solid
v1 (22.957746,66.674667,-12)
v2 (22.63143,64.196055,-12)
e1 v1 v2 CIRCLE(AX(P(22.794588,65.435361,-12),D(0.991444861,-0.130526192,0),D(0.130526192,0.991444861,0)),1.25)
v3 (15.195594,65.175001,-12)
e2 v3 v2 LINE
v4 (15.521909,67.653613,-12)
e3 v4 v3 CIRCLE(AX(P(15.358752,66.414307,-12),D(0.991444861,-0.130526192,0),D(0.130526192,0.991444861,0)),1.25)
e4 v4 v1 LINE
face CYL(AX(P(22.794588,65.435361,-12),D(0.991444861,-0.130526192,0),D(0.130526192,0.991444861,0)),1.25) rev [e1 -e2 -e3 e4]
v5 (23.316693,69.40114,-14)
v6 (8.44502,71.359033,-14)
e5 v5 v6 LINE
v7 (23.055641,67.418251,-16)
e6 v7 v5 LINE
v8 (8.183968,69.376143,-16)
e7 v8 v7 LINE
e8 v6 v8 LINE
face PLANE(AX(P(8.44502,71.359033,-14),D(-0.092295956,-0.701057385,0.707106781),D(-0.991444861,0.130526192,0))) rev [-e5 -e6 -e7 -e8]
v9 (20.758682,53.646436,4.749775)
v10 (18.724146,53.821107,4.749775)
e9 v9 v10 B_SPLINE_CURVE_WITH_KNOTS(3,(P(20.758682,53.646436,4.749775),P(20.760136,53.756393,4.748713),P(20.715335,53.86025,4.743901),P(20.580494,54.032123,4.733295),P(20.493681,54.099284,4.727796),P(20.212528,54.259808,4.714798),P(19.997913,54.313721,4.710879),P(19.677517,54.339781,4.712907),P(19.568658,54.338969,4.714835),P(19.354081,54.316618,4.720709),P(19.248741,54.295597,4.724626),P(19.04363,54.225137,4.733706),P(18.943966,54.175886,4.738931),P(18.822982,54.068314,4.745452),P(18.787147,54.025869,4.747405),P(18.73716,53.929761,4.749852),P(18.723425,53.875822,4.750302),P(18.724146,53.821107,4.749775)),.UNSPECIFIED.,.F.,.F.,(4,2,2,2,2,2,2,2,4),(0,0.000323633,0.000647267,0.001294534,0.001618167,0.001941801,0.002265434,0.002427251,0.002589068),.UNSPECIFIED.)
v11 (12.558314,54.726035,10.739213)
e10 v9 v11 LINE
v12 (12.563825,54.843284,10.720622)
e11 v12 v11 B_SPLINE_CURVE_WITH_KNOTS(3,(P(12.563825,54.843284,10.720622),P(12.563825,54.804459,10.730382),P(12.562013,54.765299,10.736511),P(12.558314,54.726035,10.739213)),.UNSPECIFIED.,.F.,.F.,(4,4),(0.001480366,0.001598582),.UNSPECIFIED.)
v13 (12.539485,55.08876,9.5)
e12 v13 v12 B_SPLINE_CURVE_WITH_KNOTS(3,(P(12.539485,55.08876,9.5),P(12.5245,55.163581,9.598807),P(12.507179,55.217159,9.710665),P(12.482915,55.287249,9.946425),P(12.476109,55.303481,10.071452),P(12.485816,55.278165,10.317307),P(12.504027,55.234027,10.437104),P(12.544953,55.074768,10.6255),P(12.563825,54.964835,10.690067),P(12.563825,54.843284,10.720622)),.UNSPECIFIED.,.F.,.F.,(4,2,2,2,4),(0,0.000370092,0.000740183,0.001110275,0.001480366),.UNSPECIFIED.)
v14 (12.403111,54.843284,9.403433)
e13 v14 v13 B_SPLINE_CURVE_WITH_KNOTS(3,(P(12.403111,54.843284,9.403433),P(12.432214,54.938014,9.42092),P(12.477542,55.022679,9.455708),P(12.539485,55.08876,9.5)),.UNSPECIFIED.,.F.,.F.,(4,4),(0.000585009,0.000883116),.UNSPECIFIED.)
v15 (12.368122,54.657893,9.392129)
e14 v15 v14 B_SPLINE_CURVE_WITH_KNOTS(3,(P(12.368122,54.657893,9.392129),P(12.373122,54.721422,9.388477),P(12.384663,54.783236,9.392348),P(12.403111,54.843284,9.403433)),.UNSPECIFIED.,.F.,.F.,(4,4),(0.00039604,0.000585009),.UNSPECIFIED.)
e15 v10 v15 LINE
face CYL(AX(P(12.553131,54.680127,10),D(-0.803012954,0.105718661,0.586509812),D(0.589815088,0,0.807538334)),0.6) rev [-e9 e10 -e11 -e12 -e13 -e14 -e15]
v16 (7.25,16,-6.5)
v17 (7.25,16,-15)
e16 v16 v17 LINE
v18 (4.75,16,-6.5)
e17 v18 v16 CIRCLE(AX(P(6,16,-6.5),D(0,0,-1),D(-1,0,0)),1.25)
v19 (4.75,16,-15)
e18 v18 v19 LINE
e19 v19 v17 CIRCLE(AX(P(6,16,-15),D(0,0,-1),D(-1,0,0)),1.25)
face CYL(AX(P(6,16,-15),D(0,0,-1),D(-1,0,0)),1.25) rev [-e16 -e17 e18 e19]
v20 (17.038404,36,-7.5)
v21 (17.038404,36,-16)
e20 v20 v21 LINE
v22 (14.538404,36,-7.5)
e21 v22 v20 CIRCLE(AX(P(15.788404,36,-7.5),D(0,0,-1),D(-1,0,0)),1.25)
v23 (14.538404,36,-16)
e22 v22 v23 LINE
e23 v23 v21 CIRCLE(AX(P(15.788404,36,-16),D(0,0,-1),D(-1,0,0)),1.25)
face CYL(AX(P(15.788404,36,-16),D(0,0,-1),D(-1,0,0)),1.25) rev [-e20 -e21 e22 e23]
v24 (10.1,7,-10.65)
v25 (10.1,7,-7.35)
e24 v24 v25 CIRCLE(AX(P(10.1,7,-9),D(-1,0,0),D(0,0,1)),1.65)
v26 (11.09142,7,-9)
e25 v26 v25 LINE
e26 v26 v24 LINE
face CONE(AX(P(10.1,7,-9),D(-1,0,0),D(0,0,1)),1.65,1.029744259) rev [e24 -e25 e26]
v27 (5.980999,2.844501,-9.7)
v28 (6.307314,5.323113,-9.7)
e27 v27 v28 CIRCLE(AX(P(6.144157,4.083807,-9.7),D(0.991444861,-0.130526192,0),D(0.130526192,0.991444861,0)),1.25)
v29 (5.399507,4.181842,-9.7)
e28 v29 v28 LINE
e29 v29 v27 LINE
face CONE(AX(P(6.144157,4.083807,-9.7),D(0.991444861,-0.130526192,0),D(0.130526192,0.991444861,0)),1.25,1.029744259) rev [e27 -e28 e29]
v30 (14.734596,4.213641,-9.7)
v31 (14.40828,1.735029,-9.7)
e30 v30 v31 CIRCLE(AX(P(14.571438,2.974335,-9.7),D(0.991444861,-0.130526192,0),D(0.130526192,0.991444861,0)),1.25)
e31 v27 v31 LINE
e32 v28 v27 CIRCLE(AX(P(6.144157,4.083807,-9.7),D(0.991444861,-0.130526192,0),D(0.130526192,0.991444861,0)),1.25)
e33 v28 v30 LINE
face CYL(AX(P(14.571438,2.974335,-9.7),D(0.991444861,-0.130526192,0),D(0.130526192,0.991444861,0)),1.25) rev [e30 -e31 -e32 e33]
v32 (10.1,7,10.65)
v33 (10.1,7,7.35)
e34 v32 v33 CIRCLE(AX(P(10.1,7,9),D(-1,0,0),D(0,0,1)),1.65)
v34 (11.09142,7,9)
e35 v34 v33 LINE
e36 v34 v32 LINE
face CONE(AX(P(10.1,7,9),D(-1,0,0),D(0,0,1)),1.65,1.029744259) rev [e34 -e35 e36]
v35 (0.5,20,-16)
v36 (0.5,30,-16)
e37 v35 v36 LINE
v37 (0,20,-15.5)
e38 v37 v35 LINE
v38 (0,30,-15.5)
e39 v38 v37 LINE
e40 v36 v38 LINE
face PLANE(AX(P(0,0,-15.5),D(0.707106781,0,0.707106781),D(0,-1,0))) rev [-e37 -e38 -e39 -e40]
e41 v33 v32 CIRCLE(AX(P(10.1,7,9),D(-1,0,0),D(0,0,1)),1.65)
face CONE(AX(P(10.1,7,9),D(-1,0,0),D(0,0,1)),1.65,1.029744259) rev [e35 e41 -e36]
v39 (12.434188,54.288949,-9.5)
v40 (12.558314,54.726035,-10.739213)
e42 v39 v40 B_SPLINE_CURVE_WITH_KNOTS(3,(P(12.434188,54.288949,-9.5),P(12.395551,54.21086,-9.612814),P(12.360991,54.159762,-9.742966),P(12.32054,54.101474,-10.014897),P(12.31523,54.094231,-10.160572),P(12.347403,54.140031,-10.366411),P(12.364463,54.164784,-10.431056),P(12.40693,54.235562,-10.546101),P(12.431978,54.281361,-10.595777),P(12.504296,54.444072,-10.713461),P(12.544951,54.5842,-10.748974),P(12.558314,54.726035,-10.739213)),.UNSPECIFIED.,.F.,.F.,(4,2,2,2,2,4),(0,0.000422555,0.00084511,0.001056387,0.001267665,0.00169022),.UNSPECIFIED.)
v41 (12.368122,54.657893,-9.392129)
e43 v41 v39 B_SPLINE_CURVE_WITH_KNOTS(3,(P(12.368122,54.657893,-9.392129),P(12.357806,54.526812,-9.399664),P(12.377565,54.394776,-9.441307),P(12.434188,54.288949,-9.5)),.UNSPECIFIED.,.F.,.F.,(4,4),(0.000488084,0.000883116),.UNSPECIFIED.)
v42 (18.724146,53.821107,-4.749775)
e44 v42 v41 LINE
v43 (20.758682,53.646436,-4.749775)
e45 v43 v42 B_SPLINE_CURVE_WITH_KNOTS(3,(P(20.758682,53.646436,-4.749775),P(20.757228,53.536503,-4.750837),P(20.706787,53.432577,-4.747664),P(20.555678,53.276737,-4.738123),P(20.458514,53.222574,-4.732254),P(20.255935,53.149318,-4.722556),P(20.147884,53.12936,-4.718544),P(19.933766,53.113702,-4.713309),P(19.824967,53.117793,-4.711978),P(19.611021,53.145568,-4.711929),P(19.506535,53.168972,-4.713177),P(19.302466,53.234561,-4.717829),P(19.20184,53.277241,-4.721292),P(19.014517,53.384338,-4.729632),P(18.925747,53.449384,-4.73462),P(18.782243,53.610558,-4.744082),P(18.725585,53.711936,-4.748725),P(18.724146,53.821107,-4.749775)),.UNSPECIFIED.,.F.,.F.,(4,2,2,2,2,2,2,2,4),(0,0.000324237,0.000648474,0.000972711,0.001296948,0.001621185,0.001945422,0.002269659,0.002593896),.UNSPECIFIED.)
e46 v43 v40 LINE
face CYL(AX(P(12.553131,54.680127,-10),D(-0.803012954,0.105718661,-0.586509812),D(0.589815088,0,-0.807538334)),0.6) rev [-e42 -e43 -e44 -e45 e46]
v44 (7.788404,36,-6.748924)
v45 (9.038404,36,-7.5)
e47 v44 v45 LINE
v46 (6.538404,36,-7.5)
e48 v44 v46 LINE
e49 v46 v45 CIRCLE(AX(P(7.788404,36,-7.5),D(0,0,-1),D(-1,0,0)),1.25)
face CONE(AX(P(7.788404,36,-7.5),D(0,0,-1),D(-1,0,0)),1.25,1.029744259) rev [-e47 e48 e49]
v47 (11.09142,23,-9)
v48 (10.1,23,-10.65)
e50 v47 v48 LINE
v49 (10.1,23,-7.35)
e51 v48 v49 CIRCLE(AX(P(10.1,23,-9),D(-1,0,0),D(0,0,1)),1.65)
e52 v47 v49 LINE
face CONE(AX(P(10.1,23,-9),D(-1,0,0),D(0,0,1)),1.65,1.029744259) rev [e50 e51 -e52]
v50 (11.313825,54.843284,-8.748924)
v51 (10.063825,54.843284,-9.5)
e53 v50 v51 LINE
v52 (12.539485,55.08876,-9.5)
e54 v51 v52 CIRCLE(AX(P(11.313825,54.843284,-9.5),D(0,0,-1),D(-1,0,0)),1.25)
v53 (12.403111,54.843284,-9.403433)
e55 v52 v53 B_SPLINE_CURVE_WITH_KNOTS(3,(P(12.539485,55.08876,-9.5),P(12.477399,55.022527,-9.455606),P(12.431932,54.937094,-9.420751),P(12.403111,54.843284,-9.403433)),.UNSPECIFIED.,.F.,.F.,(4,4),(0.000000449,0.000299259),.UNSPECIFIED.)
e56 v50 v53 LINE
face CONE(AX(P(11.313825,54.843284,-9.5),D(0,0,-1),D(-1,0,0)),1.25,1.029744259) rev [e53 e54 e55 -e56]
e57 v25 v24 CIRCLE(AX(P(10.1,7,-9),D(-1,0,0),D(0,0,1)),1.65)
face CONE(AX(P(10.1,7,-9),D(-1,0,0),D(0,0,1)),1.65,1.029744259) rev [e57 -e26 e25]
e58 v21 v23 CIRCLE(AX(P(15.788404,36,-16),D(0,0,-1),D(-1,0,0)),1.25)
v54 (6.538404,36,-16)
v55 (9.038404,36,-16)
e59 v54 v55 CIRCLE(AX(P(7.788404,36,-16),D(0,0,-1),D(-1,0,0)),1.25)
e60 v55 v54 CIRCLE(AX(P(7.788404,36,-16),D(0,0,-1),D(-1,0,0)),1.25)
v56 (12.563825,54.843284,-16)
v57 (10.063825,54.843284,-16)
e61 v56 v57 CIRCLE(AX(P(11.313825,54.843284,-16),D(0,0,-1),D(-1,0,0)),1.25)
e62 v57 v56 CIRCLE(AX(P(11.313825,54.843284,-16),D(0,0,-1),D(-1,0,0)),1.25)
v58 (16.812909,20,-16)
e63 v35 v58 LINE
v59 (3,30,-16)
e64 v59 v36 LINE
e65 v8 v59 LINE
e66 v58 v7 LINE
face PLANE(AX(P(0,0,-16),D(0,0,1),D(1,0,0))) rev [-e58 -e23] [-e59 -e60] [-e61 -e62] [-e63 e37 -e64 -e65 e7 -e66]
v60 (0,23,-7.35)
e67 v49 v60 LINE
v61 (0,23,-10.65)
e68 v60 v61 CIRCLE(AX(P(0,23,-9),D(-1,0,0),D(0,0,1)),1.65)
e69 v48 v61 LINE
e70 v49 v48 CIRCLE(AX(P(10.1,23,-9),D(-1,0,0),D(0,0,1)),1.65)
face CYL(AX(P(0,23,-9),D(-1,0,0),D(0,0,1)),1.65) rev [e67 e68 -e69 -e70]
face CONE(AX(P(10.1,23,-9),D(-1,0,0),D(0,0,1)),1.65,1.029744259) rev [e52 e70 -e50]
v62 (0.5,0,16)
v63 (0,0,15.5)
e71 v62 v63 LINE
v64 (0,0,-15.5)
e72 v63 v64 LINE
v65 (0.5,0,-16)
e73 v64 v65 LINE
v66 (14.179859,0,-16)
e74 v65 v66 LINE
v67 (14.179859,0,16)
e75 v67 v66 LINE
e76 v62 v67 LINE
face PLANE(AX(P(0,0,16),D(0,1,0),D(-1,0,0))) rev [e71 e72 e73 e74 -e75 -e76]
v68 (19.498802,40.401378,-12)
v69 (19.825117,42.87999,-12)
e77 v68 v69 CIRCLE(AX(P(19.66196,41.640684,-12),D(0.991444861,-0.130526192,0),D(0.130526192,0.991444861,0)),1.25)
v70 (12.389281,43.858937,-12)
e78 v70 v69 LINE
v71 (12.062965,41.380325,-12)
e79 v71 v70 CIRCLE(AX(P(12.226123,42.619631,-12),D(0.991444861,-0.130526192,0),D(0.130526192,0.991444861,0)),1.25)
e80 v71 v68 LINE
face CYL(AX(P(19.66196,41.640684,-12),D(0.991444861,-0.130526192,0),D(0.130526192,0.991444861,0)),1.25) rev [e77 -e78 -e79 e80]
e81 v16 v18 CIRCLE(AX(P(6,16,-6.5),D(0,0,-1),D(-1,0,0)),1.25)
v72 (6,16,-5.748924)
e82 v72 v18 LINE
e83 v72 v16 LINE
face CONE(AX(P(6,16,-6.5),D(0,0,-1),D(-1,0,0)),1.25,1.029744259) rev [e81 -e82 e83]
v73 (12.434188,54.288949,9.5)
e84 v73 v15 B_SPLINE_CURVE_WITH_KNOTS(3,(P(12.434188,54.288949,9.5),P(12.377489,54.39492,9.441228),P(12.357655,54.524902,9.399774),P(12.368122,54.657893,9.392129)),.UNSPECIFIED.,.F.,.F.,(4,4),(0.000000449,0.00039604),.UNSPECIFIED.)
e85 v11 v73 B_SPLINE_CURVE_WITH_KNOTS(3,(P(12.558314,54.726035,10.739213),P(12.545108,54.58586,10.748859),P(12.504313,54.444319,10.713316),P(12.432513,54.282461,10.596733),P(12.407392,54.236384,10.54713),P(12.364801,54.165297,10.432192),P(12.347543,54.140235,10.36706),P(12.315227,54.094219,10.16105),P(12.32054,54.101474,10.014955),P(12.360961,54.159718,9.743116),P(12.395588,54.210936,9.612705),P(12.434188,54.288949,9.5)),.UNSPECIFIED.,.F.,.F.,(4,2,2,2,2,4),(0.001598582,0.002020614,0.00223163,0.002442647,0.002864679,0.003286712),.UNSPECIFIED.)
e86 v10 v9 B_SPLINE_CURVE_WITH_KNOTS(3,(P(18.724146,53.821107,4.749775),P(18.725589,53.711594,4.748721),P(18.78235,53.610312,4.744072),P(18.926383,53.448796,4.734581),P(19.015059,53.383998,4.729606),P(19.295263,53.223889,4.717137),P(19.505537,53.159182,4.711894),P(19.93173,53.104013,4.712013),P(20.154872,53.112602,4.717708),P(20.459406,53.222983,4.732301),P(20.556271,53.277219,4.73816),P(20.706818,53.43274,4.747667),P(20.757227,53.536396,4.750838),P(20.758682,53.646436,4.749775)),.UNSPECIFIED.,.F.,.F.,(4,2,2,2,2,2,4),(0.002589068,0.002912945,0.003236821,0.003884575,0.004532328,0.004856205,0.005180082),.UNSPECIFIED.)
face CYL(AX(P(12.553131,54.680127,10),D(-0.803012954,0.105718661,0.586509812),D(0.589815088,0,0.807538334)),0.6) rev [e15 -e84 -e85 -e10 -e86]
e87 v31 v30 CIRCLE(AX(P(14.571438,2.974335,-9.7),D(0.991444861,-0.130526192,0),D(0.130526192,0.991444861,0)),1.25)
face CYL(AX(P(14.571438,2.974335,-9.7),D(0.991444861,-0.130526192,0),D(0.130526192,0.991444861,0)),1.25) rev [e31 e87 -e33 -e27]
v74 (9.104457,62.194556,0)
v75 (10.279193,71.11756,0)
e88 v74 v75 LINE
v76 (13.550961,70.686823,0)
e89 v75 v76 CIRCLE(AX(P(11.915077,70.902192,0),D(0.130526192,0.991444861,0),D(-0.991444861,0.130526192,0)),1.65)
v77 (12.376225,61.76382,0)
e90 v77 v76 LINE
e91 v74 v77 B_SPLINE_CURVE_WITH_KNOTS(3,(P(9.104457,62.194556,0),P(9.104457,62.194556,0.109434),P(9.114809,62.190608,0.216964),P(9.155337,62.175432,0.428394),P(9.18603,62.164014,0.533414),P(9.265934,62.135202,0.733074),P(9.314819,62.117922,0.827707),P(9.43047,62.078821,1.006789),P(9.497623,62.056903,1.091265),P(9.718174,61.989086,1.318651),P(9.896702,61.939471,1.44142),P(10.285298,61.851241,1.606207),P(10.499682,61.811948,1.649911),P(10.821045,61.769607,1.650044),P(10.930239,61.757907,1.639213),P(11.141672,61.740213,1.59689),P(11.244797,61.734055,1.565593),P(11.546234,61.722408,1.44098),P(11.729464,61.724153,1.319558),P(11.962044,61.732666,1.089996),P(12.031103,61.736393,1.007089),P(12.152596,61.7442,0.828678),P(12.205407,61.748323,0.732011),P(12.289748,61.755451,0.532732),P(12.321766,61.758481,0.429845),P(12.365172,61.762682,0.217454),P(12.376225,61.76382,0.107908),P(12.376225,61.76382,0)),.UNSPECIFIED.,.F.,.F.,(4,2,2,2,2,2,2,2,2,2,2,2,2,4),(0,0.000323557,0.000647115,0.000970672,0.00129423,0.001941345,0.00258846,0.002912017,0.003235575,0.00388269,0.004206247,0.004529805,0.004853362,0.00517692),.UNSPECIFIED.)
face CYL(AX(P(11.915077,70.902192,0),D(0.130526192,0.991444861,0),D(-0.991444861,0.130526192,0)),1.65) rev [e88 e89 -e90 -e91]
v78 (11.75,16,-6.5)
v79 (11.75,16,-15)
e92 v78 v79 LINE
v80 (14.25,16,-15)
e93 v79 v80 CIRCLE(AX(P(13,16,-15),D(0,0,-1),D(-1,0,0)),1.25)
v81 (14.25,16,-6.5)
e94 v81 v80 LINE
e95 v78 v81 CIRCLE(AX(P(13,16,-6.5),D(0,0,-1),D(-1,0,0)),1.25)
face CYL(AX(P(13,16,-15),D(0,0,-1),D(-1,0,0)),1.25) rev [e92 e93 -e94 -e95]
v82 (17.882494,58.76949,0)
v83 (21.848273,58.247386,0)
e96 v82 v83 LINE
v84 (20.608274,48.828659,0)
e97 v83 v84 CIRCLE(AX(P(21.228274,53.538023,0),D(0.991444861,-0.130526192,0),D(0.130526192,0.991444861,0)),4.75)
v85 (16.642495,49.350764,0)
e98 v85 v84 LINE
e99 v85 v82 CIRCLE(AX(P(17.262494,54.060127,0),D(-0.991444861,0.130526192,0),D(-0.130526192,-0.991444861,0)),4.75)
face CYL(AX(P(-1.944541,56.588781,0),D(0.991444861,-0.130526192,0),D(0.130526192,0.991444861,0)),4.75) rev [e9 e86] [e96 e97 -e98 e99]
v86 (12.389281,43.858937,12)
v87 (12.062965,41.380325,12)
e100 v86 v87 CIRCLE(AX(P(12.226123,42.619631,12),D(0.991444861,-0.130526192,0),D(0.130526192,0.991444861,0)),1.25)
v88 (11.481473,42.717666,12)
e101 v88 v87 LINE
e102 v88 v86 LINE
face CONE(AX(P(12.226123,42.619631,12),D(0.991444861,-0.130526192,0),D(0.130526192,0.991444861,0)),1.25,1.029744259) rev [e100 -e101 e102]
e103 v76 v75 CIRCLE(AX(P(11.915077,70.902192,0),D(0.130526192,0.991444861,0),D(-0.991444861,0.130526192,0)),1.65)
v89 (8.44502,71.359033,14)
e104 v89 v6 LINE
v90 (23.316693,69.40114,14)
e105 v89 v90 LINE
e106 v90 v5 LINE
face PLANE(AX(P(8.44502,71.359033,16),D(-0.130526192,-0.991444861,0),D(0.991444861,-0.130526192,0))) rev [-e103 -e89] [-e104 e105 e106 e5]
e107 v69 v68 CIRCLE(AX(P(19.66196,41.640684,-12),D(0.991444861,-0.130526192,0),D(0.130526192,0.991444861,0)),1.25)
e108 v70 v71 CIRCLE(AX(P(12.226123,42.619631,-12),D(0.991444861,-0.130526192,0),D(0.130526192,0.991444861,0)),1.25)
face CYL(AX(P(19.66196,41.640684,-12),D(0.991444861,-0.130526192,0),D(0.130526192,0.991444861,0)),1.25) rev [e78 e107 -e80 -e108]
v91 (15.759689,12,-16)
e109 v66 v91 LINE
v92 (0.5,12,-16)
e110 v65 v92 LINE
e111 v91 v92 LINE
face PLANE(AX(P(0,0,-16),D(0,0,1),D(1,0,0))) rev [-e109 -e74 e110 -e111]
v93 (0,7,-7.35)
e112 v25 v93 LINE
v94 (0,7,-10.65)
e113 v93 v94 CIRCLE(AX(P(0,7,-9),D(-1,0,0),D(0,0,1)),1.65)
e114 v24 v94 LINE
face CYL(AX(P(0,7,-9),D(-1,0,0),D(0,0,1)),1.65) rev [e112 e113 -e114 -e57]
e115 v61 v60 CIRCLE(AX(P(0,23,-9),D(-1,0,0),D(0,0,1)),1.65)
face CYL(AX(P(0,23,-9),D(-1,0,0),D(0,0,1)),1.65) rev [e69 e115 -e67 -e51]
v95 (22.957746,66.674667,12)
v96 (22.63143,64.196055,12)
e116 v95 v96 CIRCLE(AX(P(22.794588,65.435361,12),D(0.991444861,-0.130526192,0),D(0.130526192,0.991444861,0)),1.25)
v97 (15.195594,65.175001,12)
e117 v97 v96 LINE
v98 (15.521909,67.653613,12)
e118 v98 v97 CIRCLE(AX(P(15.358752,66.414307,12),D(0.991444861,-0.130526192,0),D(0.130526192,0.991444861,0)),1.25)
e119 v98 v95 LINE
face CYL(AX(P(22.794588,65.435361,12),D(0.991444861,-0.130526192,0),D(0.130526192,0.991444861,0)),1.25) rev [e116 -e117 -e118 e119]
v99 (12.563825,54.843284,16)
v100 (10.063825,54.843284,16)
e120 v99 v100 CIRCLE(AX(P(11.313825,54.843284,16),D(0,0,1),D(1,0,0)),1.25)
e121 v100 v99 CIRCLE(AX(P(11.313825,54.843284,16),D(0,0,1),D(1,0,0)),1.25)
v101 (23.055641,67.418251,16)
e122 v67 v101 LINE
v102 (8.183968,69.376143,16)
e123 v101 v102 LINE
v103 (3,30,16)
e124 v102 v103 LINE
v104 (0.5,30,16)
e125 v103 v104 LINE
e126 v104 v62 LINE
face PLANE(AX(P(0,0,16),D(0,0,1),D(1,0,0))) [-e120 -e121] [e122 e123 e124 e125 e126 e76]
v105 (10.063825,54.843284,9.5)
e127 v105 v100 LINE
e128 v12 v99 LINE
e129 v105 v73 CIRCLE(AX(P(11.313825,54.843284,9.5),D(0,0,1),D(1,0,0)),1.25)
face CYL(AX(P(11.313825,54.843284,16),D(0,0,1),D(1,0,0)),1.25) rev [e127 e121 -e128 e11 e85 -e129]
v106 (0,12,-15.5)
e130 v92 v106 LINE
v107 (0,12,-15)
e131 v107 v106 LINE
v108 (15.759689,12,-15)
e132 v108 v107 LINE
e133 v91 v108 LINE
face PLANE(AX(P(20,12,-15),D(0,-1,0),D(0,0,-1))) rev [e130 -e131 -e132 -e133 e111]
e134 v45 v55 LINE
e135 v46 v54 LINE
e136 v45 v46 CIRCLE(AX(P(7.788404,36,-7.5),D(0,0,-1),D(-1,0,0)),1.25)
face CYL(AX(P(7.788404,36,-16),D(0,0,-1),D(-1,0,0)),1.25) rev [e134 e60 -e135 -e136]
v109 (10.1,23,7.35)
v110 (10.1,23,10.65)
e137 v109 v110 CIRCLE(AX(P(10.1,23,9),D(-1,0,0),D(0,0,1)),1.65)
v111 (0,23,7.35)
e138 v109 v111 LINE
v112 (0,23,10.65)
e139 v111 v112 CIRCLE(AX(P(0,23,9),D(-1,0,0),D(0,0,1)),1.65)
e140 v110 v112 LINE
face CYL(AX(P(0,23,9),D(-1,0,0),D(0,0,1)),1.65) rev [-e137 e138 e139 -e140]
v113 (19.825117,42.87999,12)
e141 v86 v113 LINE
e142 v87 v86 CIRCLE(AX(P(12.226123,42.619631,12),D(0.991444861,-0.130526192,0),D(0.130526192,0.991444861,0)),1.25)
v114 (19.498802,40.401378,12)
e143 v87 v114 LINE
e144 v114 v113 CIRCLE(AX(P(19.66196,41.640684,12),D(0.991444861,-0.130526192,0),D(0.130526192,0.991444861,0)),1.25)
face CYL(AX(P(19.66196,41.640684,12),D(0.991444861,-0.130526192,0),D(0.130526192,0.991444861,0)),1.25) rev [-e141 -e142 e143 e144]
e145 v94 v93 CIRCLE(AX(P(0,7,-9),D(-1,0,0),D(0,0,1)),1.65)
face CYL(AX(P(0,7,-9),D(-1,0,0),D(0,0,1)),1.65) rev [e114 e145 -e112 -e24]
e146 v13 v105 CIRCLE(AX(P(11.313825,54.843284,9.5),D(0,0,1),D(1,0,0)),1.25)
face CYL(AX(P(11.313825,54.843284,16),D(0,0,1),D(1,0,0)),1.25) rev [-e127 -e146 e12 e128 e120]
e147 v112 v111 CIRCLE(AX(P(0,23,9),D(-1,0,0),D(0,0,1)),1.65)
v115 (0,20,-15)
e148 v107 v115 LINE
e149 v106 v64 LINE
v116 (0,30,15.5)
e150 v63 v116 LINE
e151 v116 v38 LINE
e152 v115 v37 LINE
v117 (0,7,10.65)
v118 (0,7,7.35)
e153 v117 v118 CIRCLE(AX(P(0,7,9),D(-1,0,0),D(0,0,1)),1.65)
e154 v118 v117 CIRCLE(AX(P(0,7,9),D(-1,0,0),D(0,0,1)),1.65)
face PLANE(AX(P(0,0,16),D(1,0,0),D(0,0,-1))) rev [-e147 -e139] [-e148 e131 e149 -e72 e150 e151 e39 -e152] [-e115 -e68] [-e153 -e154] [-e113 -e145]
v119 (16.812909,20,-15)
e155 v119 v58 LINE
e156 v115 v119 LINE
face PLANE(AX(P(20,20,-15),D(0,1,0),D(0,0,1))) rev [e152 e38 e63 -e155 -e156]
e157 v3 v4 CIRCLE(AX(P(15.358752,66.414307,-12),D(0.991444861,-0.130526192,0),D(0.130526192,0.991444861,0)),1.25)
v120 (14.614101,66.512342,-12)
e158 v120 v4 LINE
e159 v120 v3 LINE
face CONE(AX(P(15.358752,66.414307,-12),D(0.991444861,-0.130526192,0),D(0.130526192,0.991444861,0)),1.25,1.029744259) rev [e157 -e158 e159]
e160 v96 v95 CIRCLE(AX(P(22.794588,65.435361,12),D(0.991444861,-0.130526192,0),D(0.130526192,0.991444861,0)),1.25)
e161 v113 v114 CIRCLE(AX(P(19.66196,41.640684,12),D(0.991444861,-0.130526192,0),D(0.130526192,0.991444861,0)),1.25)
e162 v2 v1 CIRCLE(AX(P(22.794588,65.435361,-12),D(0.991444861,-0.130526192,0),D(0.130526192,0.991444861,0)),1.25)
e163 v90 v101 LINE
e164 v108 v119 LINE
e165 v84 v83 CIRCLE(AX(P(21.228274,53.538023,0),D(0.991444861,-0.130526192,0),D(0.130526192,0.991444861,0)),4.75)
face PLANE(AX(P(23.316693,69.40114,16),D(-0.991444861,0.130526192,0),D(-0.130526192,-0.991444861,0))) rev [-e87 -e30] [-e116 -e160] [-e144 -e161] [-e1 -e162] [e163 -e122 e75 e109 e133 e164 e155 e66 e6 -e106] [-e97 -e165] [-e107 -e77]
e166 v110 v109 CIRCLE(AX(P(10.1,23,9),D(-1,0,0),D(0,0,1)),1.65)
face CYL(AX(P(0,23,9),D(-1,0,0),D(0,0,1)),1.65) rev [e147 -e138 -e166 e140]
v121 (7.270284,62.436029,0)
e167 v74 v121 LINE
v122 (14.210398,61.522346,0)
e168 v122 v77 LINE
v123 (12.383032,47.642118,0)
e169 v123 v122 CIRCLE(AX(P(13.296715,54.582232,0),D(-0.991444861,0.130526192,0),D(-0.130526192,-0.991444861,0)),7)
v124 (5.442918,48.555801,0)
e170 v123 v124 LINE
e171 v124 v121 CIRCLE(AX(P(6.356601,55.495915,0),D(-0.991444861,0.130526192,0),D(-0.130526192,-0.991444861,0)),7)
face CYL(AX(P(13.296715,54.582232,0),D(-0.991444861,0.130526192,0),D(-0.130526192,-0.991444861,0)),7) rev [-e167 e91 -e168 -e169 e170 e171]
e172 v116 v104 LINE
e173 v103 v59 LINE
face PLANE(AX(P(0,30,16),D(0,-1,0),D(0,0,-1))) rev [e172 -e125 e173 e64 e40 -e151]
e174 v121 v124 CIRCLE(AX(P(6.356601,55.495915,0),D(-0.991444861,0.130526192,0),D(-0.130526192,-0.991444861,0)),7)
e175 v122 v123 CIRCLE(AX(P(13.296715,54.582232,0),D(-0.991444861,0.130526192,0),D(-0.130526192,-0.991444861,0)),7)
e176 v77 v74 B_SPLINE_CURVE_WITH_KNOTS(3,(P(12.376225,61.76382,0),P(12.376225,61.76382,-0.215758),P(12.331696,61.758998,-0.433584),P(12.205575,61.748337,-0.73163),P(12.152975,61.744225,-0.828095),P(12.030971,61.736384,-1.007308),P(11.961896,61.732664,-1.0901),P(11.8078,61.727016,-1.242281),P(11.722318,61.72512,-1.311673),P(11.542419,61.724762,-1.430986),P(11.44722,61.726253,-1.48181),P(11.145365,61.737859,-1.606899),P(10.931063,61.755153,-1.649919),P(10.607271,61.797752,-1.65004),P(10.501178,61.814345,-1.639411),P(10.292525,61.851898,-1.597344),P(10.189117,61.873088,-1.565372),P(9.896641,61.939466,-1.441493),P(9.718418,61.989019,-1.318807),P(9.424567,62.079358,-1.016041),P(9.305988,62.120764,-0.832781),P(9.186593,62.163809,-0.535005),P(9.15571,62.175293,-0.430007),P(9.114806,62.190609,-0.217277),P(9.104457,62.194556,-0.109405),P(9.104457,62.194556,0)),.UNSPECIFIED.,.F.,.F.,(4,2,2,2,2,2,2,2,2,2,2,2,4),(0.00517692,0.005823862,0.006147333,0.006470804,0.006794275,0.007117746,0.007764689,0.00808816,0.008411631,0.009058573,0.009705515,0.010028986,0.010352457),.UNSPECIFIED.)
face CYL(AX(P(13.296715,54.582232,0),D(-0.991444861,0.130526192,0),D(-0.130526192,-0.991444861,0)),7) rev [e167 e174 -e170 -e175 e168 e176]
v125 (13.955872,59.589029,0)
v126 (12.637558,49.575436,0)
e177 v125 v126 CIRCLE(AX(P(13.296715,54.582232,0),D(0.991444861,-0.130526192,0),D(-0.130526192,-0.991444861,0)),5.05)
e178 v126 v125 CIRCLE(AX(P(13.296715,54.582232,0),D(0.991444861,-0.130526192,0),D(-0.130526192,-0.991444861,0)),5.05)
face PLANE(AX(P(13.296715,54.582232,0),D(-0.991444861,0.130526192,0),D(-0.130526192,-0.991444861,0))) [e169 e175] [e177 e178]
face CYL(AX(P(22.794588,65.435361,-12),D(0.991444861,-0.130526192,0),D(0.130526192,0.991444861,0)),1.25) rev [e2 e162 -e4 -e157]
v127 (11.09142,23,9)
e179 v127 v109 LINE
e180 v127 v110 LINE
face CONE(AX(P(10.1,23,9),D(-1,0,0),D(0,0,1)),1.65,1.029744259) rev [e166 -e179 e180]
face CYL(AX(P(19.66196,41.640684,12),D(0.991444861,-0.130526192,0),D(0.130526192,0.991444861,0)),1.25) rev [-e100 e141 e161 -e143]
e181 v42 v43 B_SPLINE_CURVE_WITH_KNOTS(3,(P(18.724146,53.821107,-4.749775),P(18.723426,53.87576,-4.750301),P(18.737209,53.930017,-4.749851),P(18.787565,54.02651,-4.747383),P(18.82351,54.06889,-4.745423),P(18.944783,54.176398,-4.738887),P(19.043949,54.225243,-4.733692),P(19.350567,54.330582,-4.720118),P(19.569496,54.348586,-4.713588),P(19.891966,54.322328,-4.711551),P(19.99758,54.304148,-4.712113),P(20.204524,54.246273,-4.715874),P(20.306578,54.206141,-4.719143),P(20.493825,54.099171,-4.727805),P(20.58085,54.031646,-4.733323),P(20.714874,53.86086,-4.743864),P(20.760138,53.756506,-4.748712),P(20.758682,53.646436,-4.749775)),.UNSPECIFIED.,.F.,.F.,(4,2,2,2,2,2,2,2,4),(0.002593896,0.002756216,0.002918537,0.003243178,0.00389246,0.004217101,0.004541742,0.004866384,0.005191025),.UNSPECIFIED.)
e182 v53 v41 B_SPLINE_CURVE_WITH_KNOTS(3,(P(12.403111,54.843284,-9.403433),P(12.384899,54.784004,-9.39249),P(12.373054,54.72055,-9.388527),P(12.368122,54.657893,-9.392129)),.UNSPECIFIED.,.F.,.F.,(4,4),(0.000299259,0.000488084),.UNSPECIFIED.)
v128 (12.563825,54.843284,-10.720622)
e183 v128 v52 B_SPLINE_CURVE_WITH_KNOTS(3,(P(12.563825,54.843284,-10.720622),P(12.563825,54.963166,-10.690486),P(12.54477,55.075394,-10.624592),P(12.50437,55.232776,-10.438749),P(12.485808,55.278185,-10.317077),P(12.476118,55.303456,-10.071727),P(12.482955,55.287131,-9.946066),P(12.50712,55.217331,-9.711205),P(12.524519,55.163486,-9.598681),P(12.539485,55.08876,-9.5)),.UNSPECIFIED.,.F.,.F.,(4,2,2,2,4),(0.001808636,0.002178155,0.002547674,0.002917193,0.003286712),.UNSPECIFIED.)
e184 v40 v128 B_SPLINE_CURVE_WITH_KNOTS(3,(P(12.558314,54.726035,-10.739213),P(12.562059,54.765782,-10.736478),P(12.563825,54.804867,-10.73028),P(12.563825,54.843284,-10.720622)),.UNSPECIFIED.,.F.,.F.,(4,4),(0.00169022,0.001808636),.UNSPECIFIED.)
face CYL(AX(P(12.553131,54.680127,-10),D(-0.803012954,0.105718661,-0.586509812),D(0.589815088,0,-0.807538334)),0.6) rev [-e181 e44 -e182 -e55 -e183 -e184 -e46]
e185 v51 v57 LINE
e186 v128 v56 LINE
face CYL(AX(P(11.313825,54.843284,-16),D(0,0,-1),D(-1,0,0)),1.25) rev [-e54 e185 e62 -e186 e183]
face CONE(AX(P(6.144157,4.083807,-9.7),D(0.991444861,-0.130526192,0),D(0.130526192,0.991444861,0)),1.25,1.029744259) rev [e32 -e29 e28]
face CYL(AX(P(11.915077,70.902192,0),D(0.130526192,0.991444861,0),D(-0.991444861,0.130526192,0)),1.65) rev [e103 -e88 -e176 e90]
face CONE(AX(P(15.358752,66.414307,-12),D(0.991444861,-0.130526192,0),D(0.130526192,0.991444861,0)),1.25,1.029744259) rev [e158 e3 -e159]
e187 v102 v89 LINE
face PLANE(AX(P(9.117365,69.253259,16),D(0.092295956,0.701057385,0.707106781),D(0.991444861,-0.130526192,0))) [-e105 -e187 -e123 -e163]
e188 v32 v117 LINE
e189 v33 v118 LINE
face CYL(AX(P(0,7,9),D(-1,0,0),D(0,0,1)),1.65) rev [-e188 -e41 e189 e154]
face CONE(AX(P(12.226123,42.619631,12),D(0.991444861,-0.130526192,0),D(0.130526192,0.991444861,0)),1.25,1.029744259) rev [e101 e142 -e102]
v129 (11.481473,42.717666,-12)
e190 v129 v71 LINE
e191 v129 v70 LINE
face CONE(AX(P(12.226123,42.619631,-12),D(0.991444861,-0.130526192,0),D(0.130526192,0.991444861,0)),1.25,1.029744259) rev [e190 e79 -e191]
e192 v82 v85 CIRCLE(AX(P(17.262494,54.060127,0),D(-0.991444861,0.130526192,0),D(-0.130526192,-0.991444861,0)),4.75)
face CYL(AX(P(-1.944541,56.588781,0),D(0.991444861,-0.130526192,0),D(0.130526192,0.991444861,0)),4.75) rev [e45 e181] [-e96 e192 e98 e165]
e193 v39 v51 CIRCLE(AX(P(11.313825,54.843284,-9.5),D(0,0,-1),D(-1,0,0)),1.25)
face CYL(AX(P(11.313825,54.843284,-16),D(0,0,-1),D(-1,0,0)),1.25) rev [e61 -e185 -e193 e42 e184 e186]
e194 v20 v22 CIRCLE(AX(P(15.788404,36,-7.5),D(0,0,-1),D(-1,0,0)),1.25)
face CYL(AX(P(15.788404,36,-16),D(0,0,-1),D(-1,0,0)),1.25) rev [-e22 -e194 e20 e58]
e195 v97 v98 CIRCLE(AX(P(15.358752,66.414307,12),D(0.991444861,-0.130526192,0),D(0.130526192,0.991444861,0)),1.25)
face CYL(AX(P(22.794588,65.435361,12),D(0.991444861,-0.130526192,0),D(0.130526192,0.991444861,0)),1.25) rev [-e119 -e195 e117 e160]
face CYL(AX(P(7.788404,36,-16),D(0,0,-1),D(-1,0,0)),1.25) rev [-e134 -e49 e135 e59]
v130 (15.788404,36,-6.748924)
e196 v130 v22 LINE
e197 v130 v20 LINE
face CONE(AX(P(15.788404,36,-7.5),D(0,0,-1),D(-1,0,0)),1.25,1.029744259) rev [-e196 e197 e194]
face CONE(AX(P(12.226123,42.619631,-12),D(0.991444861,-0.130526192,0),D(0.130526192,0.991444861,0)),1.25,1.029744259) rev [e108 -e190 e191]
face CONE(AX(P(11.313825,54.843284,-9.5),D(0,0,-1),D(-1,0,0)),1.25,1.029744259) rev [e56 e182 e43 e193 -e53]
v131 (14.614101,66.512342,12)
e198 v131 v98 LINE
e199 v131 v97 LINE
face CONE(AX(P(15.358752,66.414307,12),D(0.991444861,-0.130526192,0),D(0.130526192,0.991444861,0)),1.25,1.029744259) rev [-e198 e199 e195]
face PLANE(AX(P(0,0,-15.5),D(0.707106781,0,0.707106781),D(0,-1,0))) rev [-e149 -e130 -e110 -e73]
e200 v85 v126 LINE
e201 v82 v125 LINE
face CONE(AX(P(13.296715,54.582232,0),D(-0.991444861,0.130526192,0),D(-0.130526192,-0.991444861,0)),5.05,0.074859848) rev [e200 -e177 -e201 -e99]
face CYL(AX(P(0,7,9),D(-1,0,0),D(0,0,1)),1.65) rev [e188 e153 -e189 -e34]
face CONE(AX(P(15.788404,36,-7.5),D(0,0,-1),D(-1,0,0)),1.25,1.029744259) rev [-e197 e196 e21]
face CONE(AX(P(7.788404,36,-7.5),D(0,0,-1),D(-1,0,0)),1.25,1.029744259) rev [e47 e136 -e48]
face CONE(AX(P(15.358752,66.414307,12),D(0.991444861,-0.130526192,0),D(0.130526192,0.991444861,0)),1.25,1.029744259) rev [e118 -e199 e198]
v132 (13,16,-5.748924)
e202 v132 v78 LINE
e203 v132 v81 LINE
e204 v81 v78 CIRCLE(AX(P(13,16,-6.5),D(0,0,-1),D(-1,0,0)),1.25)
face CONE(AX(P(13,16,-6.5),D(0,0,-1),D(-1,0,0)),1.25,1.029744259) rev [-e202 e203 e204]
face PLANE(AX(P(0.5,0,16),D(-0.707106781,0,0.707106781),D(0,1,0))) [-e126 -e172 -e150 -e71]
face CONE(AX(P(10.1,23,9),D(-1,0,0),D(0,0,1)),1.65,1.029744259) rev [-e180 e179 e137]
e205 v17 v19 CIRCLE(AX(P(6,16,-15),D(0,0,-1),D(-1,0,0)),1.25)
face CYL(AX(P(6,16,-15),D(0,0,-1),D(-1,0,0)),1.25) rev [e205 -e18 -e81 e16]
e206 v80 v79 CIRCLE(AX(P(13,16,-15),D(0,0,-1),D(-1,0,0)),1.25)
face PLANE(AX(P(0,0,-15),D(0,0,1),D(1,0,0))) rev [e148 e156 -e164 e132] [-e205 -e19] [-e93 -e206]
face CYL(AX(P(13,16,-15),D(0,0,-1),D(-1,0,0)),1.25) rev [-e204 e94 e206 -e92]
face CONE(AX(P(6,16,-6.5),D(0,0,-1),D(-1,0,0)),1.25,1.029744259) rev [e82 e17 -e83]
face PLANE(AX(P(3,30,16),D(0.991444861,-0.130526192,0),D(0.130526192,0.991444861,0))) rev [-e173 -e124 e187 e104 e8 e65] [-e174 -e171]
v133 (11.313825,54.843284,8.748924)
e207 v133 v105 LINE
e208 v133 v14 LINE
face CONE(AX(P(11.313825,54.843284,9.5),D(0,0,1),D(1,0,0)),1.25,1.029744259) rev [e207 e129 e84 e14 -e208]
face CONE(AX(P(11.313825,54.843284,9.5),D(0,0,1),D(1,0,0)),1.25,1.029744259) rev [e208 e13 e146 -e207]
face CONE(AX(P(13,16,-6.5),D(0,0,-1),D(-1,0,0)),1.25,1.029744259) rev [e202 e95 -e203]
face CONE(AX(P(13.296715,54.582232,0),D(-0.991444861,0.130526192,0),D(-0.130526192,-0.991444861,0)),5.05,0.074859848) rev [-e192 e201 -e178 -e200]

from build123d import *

# Parameters (mm, degrees)
BOSS_EXTRUDE1_DEPTH    = 16
SKETCH2_R              = 4.75
CUT_EXTRUDE1_DEPTH     = 77.207895426
CHAMFER1_SIZE          = 2
SKETCH3_R              = 7
CUT_EXTRUDE2_DEPTH     = 7
CHAMFER2_SIZE          = 4
CHAMFER2_SIZE2         = 0.3
M3_TAPPED_HOLE2_D      = 2.5
M3_TAPPED_HOLE2_DEPTH  = 7.5
M3_TAPPED_HOLE2_TIP    = 0.751075774
M4_TAPPED_HOLE1_D      = 3.3
M4_TAPPED_HOLE1_DEPTH  = 10.1
M4_TAPPED_HOLE1_TIP    = 0.991420021
CHAMFER3_SIZE          = 0.5
M4_TAPPED_HOLE3_REACH  = 76.329
M4_TAPPED_HOLE3_BORE_R = 1.65
M3_TAPPED_HOLE3_D      = 2.5
M3_TAPPED_HOLE3_DEPTH  = 8.5
M3_TAPPED_HOLE3_TIP    = 0.751075774
M3_TAPPED_HOLE4_D      = 2.5
M3_TAPPED_HOLE4_DEPTH  = 8.5
M3_TAPPED_HOLE4_TIP    = 0.751075774
SKETCH20_W             = 20
SKETCH20_H             = 8
CUT_EXTRUDE3_DEPTH     = 1
M3_TAPPED_HOLE5_D      = 2.5
M3_TAPPED_HOLE5_DEPTH  = 8.5
M3_TAPPED_HOLE5_TIP    = 0.751075774


with BuildPart() as part:
    # Sketch1 → Boss-Extrude1 (new, symmetric)
    with BuildSketch(Plane.XY):
        Polygon((0, 0), (0, 30), (3, 30), (8.445020016, 71.359033179), (23.316692936, 69.401140296), (14.179859481, 0), align=None)
    extrude(amount=BOSS_EXTRUDE1_DEPTH, both=True)

    # Sketch2 → Cut-Extrude1 (cut, through all)
    with BuildSketch(Plane(origin=(13.938275984, -1.835008845, 0), x_dir=(0, 0, -1), z_dir=(0.9914448613738108, -0.1305261922200488, 0))):
        with Locations(Location((0, 55.850843064, 0), (0, 0, 90))):
            Circle(SKETCH2_R)
    extrude(amount=-CUT_EXTRUDE1_DEPTH, mode=Mode.SUBTRACT)

    # Chamfer1
    chamfer1_edges = [part.edges().sort_by_distance(p)[0] for p in [
        (15.880856476, 70.380086738, 16),
        (15.880856476, 70.380086738, -16),
    ]]
    chamfer(chamfer1_edges, length=CHAMFER1_SIZE)

    # Sketch3 → Cut-Extrude2 (cut)
    with BuildSketch(Plane(origin=(-0.933396937, 0.122884038, 0), x_dir=(0, 0, 1), z_dir=(-0.9914448613738109, 0.13052619222004871, 0))):
        with Locations(Location((0, 55.850843064, 0), (0, 0, 270))):
            Circle(SKETCH3_R)
    extrude(amount=-CUT_EXTRUDE2_DEPTH, mode=Mode.SUBTRACT)

    # Sketch4 → M3 Tapped Hole1 (revolve, cut)
    with BuildSketch(Plane(origin=(11.313825247, 54.843284436, 16), x_dir=(0, -1, 0), z_dir=(1, 0, 0))):
        Polygon((0, 0), (0, 7.251075774), (1.25, 6.5), (1.25, 0), align=None)
    m3_tapped_hole1 = revolve(axis=Axis((11.313825247, 54.843284436, 22.35), (0, 0, -1)), mode=Mode.SUBTRACT)

    # Sketch6 → Cut-Revolve1 (revolve, cut)
    with BuildSketch(Plane(origin=(7.289997877, 55.373031359, 0), x_dir=(0.9914448613738107, -0.1305261922200494, 0), z_dir=(0.1305261922200494, 0.9914448613738107, 0)), mode=Mode.PRIVATE) as cut_revolve1_sk:
        Polygon((4.058548818, -10.905172414), (14.587796398, -3.280544856), (14.939702285, -3.766510129), (4.410454705, -11.391137687), align=None)
    cut_revolve1 = revolve(cut_revolve1_sk.sketch.rotate(Axis((12.553131324, 54.680126696, 10), (0.80301295441403, -0.10571866104363936, -0.5865098121518437)), 355.584640013), axis=Axis((12.553131324, 54.680126696, 10), (0.80301295441403, -0.10571866104363936, -0.5865098121518437)), mode=Mode.SUBTRACT)

    # Mirror1: M3 Tapped Hole1, Cut-Revolve1 across plane
    add(m3_tapped_hole1.mirror(Plane.XY), mode=Mode.SUBTRACT)
    add(cut_revolve1.mirror(Plane.XY), mode=Mode.SUBTRACT)

    # Chamfer2
    chamfer2_edges = [part.edges().sort_by_distance(p)[0] for p in [
        (12.676715557, 49.87286896, 0),
    ]]
    chamfer2_side = [part.faces().sort_by_distance(p)[0] for p in [
        (16.642495002, 49.350764192, 0),
    ]]
    chamfer(chamfer2_edges, length=CHAMFER2_SIZE, length2=CHAMFER2_SIZE2, reference=chamfer2_side[0])

    # M3 Tapped Hole2
    with Locations(Plane(origin=(13.938275984, -1.835008845, 0), x_dir=(0, 0, -1), z_dir=(0.9914448613738107, -0.13052619222004877, 0))):
        with Locations((-12, 67.850843064), (12, 67.850843064), (12, 43.850843064), (-12, 43.850843064)):
            Hole(M3_TAPPED_HOLE2_D / 2, depth=M3_TAPPED_HOLE2_DEPTH)
            with Locations((0, 0, -(M3_TAPPED_HOLE2_DEPTH + M3_TAPPED_HOLE2_TIP / 2))):  # 118° drill point
                Cone(0, M3_TAPPED_HOLE2_D / 2, M3_TAPPED_HOLE2_TIP, mode=Mode.SUBTRACT)

    # M4 Tapped Hole1
    with Locations(Plane.ZY):
        with Locations((-9, 23), (9, 23), (9, 7), (-9, 7)):
            Hole(M4_TAPPED_HOLE1_D / 2, depth=M4_TAPPED_HOLE1_DEPTH)
            with Locations((0, 0, -(M4_TAPPED_HOLE1_DEPTH + M4_TAPPED_HOLE1_TIP / 2))):  # 118° drill point
                Cone(0, M4_TAPPED_HOLE1_D / 2, M4_TAPPED_HOLE1_TIP, mode=Mode.SUBTRACT)

    # Chamfer3
    chamfer3_edges = [part.edges().sort_by_distance(p)[0] for p in [
        (0, 15, 16),
        (0, 15, -16),
    ]]
    chamfer(chamfer3_edges, length=CHAMFER3_SIZE)

    # M4 Tapped Hole3 bore → M4 Tapped Hole3 (cut, up to next)
    with BuildSketch(Plane(origin=(9.378416953, 71.236149141, 0), x_dir=(0.9914448613738107, -0.1305261922200494, 0), z_dir=(0.1305261922200494, 0.9914448613738107, 0)), mode=Mode.PRIVATE) as m4_tapped_hole3_sk1:
        with Locations((2.558548818, 0)):
            Circle(M4_TAPPED_HOLE3_BORE_R)
    m4_tapped_hole3_tool1 = extrude(m4_tapped_hole3_sk1.sketch, amount=-M4_TAPPED_HOLE3_REACH, mode=Mode.PRIVATE) & part.part
    add(m4_tapped_hole3_tool1.solids().sort_by_distance((11.915077, 70.902192, 0))[0], mode=Mode.SUBTRACT)

    # M3 Tapped Hole3
    with Locations(Plane(origin=(13.938275984, -1.835008845, 0), x_dir=(0, 0, -1), z_dir=(0.9914448613738108, -0.1305261922200488, 0))):
        with Locations((9.7, 4.850843064)):
            Hole(M3_TAPPED_HOLE3_D / 2, depth=M3_TAPPED_HOLE3_DEPTH)
            with Locations((0, 0, -(M3_TAPPED_HOLE3_DEPTH + M3_TAPPED_HOLE3_TIP / 2))):  # 118° drill point
                Cone(0, M3_TAPPED_HOLE3_D / 2, M3_TAPPED_HOLE3_TIP, mode=Mode.SUBTRACT)

    # M3 Tapped Hole4
    with Locations(Plane(origin=(0, 0, -16), x_dir=(-1, 0, 0), z_dir=(0, 0, -1))):
        with Locations((-15.788403885, 36), (-7.788403885, 36)):
            Hole(M3_TAPPED_HOLE4_D / 2, depth=M3_TAPPED_HOLE4_DEPTH)
            with Locations((0, 0, -(M3_TAPPED_HOLE4_DEPTH + M3_TAPPED_HOLE4_TIP / 2))):  # 118° drill point
                Cone(0, M3_TAPPED_HOLE4_D / 2, M3_TAPPED_HOLE4_TIP, mode=Mode.SUBTRACT)

    # Sketch20 → Cut-Extrude3 (cut)
    with BuildSketch(Plane(origin=(0, 0, -16), x_dir=(-1, 0, 0), z_dir=(0, 0, -1))):
        with Locations((-10, 16)):
            Rectangle(SKETCH20_W, SKETCH20_H)
    extrude(amount=-CUT_EXTRUDE3_DEPTH, mode=Mode.SUBTRACT)

    # M3 Tapped Hole5
    with Locations(Plane(origin=(0, 0, -15), x_dir=(-1, 0, 0), z_dir=(0, 0, -1))):
        with Locations((-13, 16), (-6, 16)):
            Hole(M3_TAPPED_HOLE5_D / 2, depth=M3_TAPPED_HOLE5_DEPTH)
            with Locations((0, 0, -(M3_TAPPED_HOLE5_DEPTH + M3_TAPPED_HOLE5_TIP / 2))):  # 118° drill point
                Cone(0, M3_TAPPED_HOLE5_D / 2, M3_TAPPED_HOLE5_TIP, mode=Mode.SUBTRACT)


solid = part.part
